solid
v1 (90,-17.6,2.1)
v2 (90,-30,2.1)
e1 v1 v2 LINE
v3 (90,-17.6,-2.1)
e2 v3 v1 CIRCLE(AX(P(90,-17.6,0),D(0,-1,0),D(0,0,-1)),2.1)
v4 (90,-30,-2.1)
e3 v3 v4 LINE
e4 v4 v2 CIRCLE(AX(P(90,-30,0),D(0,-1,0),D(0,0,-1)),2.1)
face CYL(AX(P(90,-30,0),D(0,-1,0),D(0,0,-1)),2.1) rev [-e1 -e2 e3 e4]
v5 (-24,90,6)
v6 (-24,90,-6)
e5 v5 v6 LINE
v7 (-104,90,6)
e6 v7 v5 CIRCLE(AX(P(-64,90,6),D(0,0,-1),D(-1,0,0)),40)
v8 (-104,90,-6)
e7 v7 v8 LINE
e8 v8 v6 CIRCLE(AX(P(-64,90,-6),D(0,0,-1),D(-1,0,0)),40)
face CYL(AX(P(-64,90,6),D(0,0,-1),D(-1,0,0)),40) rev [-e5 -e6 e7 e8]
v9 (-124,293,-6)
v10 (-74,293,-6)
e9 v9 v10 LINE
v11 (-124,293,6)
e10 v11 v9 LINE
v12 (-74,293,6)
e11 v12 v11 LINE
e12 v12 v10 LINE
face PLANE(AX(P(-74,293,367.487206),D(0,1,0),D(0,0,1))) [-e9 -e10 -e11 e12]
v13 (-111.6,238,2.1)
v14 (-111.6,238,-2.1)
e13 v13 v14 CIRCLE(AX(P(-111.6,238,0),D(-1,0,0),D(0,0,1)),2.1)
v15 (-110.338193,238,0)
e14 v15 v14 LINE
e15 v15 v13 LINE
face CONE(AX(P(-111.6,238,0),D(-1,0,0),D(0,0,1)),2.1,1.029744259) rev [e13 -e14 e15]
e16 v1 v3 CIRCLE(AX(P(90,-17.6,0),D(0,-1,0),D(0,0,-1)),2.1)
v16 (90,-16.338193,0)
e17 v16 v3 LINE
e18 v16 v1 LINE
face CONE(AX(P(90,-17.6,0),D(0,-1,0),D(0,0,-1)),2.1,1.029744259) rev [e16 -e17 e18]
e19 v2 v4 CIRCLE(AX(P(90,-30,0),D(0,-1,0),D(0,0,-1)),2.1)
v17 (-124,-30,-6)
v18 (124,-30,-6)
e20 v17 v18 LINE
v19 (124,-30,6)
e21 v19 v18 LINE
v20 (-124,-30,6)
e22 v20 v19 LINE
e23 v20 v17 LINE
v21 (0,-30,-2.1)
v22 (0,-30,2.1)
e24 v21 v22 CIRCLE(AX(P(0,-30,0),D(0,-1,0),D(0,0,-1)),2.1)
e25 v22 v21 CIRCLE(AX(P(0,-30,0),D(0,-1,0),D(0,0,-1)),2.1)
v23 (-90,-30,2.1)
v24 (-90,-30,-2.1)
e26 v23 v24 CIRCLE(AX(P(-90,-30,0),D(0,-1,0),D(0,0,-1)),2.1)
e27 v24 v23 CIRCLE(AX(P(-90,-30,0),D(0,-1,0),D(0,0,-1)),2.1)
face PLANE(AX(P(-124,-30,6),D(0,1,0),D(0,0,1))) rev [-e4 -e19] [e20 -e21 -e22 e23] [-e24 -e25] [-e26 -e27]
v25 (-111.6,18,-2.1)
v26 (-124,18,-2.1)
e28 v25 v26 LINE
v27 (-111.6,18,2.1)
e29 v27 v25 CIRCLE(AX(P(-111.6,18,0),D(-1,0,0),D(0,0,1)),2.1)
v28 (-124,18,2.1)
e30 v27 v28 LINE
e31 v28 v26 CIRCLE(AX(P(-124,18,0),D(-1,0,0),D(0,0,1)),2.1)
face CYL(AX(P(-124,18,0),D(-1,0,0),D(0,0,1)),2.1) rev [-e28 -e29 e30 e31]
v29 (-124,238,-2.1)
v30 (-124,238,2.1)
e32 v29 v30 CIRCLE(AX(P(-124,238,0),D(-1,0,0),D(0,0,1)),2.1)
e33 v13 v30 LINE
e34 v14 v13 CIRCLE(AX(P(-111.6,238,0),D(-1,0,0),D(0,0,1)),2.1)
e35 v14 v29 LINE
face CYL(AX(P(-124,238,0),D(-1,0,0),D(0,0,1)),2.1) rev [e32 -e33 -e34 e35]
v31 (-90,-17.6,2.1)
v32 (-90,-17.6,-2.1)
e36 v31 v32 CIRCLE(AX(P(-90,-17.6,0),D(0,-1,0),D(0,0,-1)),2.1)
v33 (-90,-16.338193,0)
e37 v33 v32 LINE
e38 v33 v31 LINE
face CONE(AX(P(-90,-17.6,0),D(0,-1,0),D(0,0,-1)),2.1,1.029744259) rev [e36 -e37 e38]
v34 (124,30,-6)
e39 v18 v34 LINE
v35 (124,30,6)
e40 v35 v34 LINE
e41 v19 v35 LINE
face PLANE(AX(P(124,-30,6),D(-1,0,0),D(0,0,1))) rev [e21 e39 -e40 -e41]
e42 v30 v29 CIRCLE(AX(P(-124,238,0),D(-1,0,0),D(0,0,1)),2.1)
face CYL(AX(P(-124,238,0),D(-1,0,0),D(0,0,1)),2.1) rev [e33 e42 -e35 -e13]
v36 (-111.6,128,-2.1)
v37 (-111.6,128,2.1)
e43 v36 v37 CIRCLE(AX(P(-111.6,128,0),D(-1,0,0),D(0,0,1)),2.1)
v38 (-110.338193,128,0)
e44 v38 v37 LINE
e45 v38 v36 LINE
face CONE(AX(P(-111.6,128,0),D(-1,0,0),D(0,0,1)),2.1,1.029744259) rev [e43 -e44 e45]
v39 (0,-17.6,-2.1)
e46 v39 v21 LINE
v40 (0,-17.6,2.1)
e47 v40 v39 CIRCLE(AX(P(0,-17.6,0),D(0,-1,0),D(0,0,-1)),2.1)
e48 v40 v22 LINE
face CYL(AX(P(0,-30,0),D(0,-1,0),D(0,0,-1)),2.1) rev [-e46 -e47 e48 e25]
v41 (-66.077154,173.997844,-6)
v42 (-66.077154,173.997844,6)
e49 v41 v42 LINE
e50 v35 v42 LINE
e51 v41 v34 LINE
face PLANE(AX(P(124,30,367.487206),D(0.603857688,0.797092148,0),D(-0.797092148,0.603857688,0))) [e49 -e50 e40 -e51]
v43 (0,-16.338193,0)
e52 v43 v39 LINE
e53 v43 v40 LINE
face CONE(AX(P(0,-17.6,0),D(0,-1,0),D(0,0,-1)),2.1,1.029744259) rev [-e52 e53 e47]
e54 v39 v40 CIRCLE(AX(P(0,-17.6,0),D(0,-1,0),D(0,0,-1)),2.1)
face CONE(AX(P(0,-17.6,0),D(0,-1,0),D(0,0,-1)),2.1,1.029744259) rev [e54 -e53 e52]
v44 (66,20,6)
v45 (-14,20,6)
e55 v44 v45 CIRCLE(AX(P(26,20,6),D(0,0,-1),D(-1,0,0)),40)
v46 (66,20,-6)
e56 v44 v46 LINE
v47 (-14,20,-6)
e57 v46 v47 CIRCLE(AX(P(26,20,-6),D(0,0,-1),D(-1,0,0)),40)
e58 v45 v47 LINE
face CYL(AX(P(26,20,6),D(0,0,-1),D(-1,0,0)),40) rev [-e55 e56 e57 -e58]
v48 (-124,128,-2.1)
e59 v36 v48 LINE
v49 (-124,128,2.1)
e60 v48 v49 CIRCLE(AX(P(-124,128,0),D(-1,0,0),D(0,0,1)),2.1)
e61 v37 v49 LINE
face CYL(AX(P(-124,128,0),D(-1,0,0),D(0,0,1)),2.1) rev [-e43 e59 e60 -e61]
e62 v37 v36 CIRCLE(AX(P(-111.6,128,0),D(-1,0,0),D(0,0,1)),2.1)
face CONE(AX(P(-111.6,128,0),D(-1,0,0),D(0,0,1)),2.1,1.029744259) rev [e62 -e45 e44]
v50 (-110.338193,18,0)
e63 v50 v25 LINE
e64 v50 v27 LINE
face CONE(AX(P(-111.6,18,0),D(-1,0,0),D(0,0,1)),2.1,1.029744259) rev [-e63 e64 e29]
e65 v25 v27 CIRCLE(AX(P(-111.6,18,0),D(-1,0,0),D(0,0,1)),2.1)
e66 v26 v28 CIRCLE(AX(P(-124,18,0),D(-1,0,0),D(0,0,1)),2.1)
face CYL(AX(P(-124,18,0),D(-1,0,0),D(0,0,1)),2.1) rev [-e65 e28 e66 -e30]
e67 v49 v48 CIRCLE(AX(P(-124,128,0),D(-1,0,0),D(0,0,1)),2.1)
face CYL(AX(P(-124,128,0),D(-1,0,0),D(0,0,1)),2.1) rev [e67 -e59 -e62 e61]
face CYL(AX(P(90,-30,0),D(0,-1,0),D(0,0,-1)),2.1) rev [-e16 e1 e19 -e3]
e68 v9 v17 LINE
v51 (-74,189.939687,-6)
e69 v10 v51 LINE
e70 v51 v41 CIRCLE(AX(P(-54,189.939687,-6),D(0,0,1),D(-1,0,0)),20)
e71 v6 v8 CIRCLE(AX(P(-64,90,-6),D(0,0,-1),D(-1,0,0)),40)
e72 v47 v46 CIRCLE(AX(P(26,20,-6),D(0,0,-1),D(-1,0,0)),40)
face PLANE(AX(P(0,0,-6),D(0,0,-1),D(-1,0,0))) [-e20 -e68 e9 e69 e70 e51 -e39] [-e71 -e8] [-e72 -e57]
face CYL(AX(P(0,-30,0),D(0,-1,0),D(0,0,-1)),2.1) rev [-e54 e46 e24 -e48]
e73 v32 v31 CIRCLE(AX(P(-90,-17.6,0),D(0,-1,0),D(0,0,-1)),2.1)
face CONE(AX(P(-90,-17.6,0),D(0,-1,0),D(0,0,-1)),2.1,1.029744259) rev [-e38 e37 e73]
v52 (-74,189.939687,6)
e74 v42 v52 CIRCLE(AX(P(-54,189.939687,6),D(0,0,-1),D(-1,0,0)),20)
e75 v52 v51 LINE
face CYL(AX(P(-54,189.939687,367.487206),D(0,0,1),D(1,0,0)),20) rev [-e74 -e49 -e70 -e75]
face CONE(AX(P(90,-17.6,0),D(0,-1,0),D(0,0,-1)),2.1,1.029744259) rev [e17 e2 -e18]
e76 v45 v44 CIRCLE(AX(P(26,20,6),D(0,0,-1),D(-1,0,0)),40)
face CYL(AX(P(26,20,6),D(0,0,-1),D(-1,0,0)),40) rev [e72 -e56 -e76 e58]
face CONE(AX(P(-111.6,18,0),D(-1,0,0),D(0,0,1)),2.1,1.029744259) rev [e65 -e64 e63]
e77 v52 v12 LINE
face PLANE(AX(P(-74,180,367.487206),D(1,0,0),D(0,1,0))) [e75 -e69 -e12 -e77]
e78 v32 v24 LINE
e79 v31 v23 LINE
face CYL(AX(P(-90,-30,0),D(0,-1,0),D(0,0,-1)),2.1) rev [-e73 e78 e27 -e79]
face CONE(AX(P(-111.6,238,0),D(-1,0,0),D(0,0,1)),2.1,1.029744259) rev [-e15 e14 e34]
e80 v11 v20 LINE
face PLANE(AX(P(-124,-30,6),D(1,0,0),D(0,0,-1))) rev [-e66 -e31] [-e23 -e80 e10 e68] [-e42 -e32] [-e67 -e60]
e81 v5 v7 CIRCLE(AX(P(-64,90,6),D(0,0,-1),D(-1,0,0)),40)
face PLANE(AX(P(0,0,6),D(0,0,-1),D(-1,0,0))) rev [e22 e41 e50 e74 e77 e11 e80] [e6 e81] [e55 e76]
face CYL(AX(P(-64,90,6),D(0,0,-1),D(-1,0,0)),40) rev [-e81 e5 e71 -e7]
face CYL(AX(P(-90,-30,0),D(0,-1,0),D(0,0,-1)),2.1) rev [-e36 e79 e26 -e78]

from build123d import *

# Parameters (mm, degrees)
SKETCH_1_W             = 248
SKETCH_1_H             = 60
EXTRUDE_1_DEPTH        = 6
EXTRUDE_2_DEPTH        = 12
FILLET_1_R             = 20
SKETCH_3_R             = 40
CUT_EXTRUDE_1_DEPTH    = 319.384987083
HOLE_WIZARD_M5_1_D     = 4.2
HOLE_WIZARD_M5_1_DEPTH = 12.4
HOLE_WIZARD_M5_1_TIP   = 1.2618073
HOLE_WIZARD_M5_2_D     = 4.2
HOLE_WIZARD_M5_2_DEPTH = 12.4
HOLE_WIZARD_M5_2_TIP   = 1.2618073


with BuildPart() as part:
    # 草图1 → 凸台-拉伸1 (new, symmetric)
    with BuildSketch(Plane.XY):
        Rectangle(SKETCH_1_W, SKETCH_1_H)
    extrude(amount=EXTRUDE_1_DEPTH, both=True)

    # 草图2 → 凸台-拉伸2 (add)
    with BuildSketch(Plane(origin=(0, 0, -6), x_dir=(-1, 0, 0), z_dir=(0, 0, -1))):
        Polygon((-124, 30), (74, 180), (74, 293), (124, 293), (124, 30), align=None)
    extrude(amount=-EXTRUDE_2_DEPTH)

    # 圆角1
    fillet_1_edges = [part.edges().sort_by_distance(p)[0] for p in [
        (-74, 180, 0),
    ]]
    fillet(fillet_1_edges, radius=FILLET_1_R)

    # 草图3 → 切除-拉伸1 (cut, through all)
    with BuildSketch(Plane(origin=(0, 0, -6), x_dir=(-1, 0, 0), z_dir=(0, 0, -1))):
        with Locations((-26, 20)):
            Circle(SKETCH_3_R)
        with Locations((64, 90)):
            Circle(SKETCH_3_R)
    extrude(amount=-CUT_EXTRUDE_1_DEPTH, mode=Mode.SUBTRACT)

    # M5 螺纹孔1
    with Locations(Plane(origin=(0, -30, 0), x_dir=(-1, 0, 0), z_dir=(0, -1, 0))):
        with Locations((-90, 0), (0, 0), (90, 0)):
            Hole(HOLE_WIZARD_M5_1_D / 2, depth=HOLE_WIZARD_M5_1_DEPTH)
            with Locations((0, 0, -(HOLE_WIZARD_M5_1_DEPTH + HOLE_WIZARD_M5_1_TIP / 2))):  # 118° drill point
                Cone(0, HOLE_WIZARD_M5_1_D / 2, HOLE_WIZARD_M5_1_TIP, mode=Mode.SUBTRACT)

    # M5 螺纹孔2
    with Locations(Plane.ZY.offset(124)):
        with Locations((0, 238), (0, 128), (0, 18)):
            Hole(HOLE_WIZARD_M5_2_D / 2, depth=HOLE_WIZARD_M5_2_DEPTH)
            with Locations((0, 0, -(HOLE_WIZARD_M5_2_DEPTH + HOLE_WIZARD_M5_2_TIP / 2))):  # 118° drill point
                Cone(0, HOLE_WIZARD_M5_2_D / 2, HOLE_WIZARD_M5_2_TIP, mode=Mode.SUBTRACT)


solid = part.part
